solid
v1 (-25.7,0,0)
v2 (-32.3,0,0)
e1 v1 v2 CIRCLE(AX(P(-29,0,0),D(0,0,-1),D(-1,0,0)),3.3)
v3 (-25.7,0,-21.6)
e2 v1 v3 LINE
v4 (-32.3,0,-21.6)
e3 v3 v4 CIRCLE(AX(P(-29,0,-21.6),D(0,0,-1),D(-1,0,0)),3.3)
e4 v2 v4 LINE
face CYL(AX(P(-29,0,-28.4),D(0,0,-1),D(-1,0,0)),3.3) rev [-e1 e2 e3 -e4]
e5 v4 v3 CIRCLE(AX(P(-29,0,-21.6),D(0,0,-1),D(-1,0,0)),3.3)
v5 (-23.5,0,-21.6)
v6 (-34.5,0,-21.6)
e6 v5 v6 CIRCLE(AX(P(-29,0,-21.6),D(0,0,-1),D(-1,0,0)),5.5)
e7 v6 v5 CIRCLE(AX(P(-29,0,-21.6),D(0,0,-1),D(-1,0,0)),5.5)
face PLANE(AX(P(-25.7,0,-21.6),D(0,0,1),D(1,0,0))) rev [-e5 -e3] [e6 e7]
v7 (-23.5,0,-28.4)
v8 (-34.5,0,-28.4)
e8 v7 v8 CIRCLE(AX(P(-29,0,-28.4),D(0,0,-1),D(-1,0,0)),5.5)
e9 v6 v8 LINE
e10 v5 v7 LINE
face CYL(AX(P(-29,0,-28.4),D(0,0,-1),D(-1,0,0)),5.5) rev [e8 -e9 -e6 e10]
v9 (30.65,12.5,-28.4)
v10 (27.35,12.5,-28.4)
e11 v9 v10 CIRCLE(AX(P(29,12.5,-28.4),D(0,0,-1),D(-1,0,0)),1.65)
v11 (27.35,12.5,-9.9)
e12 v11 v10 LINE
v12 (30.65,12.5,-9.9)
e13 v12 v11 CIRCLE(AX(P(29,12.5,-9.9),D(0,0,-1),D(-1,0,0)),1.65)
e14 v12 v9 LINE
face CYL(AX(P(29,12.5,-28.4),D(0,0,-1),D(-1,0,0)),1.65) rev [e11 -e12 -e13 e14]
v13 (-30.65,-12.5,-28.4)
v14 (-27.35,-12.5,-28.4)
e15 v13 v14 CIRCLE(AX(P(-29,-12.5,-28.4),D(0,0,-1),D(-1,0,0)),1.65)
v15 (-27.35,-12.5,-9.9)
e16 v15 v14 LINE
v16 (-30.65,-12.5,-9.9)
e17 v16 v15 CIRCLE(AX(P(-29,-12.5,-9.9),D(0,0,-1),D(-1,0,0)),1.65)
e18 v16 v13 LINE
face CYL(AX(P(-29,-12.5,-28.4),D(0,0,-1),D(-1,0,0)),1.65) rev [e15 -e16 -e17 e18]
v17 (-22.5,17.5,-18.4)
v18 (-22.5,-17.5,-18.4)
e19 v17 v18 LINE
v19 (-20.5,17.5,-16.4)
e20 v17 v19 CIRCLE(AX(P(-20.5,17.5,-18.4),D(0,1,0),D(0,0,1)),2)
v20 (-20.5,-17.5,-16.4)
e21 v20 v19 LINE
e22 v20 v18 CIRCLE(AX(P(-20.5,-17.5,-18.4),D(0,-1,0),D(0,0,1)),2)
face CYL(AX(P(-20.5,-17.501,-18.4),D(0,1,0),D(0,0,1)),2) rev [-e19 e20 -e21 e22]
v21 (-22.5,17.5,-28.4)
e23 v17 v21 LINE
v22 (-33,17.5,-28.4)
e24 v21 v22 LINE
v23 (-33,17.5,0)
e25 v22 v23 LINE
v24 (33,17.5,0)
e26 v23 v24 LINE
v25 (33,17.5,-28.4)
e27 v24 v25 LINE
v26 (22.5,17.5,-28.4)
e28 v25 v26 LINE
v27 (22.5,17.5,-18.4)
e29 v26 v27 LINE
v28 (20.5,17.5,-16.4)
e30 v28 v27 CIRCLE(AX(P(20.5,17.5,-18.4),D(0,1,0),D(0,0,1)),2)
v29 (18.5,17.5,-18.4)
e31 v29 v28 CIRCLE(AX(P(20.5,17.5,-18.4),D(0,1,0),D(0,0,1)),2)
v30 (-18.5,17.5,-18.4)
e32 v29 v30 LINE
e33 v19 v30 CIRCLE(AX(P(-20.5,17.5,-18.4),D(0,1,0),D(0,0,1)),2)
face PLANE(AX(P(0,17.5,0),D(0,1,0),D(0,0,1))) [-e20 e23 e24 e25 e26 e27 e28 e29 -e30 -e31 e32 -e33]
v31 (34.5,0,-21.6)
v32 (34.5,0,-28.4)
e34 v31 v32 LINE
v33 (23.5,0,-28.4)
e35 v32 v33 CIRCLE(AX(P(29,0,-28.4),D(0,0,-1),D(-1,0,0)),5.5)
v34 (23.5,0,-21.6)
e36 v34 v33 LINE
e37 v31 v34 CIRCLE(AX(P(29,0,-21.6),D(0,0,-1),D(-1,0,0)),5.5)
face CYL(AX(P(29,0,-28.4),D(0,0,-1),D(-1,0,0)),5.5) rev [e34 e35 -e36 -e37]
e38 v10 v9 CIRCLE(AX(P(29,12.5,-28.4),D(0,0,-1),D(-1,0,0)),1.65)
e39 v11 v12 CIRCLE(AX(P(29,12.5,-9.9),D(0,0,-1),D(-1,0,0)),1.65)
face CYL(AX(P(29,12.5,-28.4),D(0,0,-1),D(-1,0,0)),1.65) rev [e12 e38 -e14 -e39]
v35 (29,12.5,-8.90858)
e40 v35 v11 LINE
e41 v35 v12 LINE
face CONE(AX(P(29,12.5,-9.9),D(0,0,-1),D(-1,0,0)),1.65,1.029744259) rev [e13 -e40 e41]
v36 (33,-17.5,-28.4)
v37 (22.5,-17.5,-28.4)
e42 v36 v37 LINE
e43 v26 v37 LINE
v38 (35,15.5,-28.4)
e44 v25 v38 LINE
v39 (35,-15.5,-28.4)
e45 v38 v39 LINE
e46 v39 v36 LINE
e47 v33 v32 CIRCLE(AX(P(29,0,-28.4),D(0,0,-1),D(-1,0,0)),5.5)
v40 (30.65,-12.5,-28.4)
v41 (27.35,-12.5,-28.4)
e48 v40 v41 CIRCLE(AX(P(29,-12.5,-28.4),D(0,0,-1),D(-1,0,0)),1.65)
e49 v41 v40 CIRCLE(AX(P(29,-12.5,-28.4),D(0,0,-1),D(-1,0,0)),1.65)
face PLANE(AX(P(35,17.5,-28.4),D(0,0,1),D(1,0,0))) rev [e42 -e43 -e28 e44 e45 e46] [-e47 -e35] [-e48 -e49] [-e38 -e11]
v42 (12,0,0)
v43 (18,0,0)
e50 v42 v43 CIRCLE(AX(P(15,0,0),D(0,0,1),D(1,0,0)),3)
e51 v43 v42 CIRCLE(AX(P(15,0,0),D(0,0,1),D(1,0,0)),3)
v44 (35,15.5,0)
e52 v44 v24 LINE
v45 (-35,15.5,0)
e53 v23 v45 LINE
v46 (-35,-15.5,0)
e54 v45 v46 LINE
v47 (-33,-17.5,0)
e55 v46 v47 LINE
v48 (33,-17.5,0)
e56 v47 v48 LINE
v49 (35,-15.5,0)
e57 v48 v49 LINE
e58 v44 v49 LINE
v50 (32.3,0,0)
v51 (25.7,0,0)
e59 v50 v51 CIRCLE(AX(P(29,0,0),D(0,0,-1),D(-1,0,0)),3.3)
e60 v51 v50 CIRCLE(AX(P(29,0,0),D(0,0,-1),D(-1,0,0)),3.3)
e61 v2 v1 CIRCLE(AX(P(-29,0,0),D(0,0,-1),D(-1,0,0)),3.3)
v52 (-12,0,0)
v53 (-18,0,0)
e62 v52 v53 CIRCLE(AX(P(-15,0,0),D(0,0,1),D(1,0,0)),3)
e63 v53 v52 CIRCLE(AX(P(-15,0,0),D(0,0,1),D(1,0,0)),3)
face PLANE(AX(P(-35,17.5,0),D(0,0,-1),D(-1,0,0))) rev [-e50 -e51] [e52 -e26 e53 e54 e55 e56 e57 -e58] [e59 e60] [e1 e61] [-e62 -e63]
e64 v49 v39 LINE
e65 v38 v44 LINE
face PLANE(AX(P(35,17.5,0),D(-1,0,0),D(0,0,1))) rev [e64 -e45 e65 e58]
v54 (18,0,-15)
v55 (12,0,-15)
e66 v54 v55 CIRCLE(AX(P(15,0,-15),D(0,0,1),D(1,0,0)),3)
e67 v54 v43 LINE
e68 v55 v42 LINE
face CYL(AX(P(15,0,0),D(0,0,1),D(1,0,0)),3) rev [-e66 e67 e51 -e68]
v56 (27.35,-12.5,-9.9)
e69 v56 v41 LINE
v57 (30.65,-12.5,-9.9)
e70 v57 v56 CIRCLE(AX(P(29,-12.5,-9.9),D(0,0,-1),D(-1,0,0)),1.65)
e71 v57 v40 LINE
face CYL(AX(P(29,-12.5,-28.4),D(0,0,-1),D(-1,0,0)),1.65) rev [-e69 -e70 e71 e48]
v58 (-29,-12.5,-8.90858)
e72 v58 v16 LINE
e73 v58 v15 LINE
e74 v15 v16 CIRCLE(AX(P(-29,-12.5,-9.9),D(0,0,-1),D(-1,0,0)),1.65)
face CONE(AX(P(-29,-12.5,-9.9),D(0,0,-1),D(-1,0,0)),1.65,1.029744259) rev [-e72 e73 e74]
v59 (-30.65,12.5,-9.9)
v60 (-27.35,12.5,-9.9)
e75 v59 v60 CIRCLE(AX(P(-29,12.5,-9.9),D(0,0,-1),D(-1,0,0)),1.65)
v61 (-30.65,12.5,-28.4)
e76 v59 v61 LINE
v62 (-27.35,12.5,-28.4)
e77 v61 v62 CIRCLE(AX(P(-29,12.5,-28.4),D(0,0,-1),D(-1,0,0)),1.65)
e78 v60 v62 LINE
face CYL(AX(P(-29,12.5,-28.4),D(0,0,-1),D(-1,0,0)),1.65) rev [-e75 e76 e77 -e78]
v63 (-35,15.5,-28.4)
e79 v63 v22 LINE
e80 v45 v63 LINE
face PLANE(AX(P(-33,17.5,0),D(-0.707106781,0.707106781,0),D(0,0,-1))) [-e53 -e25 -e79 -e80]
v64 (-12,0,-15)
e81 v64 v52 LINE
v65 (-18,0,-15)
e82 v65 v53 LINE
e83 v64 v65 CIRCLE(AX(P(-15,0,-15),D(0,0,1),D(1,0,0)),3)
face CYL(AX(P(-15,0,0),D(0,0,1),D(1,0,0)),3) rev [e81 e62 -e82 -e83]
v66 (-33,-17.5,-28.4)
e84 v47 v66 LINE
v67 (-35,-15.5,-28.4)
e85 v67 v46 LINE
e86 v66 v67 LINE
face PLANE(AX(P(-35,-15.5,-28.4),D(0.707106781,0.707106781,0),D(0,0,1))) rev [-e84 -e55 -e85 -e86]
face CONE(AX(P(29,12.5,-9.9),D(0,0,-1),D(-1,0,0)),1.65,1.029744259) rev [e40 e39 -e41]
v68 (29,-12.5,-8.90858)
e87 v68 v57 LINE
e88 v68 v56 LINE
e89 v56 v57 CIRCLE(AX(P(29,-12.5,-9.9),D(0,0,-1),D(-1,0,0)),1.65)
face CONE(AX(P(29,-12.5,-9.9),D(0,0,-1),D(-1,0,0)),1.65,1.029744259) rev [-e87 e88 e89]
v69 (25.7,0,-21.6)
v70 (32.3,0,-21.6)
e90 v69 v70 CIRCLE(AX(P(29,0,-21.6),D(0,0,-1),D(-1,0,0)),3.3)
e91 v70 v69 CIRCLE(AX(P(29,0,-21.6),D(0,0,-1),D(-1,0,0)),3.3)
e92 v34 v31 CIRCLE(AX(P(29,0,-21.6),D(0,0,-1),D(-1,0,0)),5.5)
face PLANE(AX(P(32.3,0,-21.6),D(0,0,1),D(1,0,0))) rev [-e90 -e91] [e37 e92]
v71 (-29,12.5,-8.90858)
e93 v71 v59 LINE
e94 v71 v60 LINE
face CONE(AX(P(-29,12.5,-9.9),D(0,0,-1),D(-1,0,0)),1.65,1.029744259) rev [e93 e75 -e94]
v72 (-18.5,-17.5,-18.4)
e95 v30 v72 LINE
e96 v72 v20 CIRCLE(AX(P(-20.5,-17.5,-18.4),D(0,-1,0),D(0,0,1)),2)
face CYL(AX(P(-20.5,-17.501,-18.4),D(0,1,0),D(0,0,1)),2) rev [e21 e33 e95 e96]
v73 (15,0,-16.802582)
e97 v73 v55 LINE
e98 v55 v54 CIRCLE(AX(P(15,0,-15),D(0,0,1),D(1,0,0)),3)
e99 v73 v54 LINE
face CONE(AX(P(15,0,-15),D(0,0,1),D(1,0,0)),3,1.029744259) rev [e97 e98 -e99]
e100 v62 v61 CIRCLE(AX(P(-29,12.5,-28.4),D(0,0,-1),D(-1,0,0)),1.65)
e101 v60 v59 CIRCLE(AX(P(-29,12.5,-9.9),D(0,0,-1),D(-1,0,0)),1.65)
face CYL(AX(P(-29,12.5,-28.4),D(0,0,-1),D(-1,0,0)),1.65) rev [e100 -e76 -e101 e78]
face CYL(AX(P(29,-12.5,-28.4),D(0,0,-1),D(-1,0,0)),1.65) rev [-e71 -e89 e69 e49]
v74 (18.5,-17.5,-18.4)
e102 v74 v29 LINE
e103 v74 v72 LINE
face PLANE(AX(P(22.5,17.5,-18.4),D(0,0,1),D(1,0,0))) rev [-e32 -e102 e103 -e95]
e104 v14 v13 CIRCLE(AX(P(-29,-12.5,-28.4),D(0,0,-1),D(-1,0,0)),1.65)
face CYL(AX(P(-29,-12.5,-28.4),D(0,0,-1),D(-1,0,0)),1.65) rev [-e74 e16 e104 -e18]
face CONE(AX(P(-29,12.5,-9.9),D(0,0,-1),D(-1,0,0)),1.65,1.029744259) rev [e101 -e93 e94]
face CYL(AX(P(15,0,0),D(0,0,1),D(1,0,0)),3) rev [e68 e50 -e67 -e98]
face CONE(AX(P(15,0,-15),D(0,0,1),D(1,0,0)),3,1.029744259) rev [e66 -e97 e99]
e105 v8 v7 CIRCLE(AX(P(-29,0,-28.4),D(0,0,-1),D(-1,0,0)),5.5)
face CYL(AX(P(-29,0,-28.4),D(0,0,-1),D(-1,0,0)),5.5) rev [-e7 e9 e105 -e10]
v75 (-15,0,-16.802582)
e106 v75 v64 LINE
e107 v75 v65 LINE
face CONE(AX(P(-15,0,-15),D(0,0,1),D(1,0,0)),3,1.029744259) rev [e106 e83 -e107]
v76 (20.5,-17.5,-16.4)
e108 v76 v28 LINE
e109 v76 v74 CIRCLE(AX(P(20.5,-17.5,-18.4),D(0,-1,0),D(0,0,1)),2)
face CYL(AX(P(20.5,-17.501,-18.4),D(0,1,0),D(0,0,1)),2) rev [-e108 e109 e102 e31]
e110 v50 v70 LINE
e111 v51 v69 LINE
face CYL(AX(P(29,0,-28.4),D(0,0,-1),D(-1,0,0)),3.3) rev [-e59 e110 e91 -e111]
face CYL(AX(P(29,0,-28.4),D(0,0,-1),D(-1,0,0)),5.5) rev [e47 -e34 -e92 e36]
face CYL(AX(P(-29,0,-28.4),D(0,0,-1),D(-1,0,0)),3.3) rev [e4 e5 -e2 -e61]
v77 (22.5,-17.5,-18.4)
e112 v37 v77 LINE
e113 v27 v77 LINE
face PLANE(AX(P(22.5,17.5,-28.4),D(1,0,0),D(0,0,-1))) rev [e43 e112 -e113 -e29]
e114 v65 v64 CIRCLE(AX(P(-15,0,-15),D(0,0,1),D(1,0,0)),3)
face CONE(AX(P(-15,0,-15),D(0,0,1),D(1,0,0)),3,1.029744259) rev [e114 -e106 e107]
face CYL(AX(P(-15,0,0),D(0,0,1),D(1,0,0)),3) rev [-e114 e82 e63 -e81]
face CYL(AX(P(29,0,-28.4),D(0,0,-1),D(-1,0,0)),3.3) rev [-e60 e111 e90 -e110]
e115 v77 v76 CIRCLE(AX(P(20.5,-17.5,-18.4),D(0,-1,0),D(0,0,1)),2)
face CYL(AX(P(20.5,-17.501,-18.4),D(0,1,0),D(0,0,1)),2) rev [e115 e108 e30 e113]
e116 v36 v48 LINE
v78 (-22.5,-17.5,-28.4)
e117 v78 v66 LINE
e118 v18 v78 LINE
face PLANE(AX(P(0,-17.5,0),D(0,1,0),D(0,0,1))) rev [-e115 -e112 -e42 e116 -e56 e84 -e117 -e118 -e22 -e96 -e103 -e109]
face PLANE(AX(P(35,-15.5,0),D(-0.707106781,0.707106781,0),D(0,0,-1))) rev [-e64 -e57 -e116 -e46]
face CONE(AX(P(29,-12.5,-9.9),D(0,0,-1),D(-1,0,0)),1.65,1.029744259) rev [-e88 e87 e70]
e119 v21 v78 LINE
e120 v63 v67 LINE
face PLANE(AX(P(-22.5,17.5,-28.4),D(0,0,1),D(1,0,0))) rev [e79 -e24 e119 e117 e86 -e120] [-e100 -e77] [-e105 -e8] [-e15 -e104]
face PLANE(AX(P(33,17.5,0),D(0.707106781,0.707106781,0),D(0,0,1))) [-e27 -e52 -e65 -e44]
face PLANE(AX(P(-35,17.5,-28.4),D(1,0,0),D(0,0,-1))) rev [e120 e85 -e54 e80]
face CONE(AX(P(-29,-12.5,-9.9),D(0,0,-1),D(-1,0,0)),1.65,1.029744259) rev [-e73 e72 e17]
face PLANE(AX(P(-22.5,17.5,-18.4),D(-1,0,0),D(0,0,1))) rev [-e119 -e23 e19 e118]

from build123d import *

# Parameters (mm, degrees)
EXTRUDE_1_DEPTH              = 17.5
CUT_EXTRUDE_1_REACH          = 59.066
SKETCH_2_R                   = 2
CHAMFER_1_SIZE               = 2
F_6_0MM_1_D                  = 6
F_6_0MM_1_DEPTH              = 15
F_6_0MM_1_TIP                = 1.802581857
HOLE_WIZARD_M6_1_D           = 6.6
HOLE_WIZARD_M6_1_CBORE_D     = 11
HOLE_WIZARD_M6_1_CBORE_DEPTH = 6.8
HOLE_WIZARD_M4_1_D           = 3.3
HOLE_WIZARD_M4_1_DEPTH       = 18.5
HOLE_WIZARD_M4_1_TIP         = 0.991420021


with BuildPart() as part:
    # 草图1 → 凸台-拉伸1 (new, symmetric)
    with BuildSketch(Plane(origin=(0, 0, 0), x_dir=(1, 0, 0), z_dir=(0, 1, 0))):
        Polygon((-35, 0), (35, 0), (35, 28.4), (22.5, 28.4), (22.5, 18.4), (-22.5, 18.4), (-22.5, 28.4), (-35, 28.4), align=None)
    extrude(amount=EXTRUDE_1_DEPTH, both=True)

    # 草图2 → 切除-拉伸1 (cut, up to next)
    with BuildSketch(Plane(origin=(0, 17.5, 0), x_dir=(1, 0, 0), z_dir=(0, 1, 0)), mode=Mode.PRIVATE) as cut_extrude_1_sk1:
        with Locations((20.5, 18.4)):
            Circle(SKETCH_2_R)
    cut_extrude_1_tool1 = extrude(cut_extrude_1_sk1.sketch, amount=-CUT_EXTRUDE_1_REACH, mode=Mode.PRIVATE) & part.part
    # 草图2 → 切除-拉伸1 (cut, up to next)
    with BuildSketch(Plane(origin=(0, 17.5, 0), x_dir=(1, 0, 0), z_dir=(0, 1, 0)), mode=Mode.PRIVATE) as cut_extrude_1_sk2:
        with Locations((-20.5, 18.4)):
            Circle(SKETCH_2_R)
    cut_extrude_1_tool2 = extrude(cut_extrude_1_sk2.sketch, amount=-CUT_EXTRUDE_1_REACH, mode=Mode.PRIVATE) & part.part
    add(cut_extrude_1_tool1.solids().sort_by_distance((20.5, 17.5, -18.4))[0], mode=Mode.SUBTRACT)
    add(cut_extrude_1_tool2.solids().sort_by_distance((-20.5, 17.5, -18.4))[0], mode=Mode.SUBTRACT)

    # 倒角1
    chamfer_1_edges = [part.edges().sort_by_distance(p)[0] for p in [
        (35, -17.5, -14.2),
        (-35, -17.5, -14.2),
        (35, 17.5, -14.2),
        (-35, 17.5, -14.2),
    ]]
    chamfer(chamfer_1_edges, length=CHAMFER_1_SIZE)

    # Ø6.0mm 暗销孔1
    with Locations(Plane.XY):
        with Locations((-15, 0), (15, 0)):
            Hole(F_6_0MM_1_D / 2, depth=F_6_0MM_1_DEPTH)
            with Locations((0, 0, -(F_6_0MM_1_DEPTH + F_6_0MM_1_TIP / 2))):  # 118° drill point
                Cone(0, F_6_0MM_1_D / 2, F_6_0MM_1_TIP, mode=Mode.SUBTRACT)

    # M6 六角圆柱头螺钉的柱形沉头孔1 (through all)
    with Locations(Plane(origin=(0, 0, -28.4), x_dir=(-1, 0, 0), z_dir=(0, 0, -1))):
        with Locations((-29, 0), (29, 0)):
            CounterBoreHole(HOLE_WIZARD_M6_1_D / 2, HOLE_WIZARD_M6_1_CBORE_D / 2, HOLE_WIZARD_M6_1_CBORE_DEPTH)

    # M4 螺纹孔1
    with Locations(Plane(origin=(0, 0, -28.4), x_dir=(-1, 0, 0), z_dir=(0, 0, -1))):
        with Locations((-29, 12.5), (-29, -12.5), (29, 12.5), (29, -12.5)):
            Hole(HOLE_WIZARD_M4_1_D / 2, depth=HOLE_WIZARD_M4_1_DEPTH)
            with Locations((0, 0, -(HOLE_WIZARD_M4_1_DEPTH + HOLE_WIZARD_M4_1_TIP / 2))):  # 118° drill point
                Cone(0, HOLE_WIZARD_M4_1_D / 2, HOLE_WIZARD_M4_1_TIP, mode=Mode.SUBTRACT)


solid = part.part
